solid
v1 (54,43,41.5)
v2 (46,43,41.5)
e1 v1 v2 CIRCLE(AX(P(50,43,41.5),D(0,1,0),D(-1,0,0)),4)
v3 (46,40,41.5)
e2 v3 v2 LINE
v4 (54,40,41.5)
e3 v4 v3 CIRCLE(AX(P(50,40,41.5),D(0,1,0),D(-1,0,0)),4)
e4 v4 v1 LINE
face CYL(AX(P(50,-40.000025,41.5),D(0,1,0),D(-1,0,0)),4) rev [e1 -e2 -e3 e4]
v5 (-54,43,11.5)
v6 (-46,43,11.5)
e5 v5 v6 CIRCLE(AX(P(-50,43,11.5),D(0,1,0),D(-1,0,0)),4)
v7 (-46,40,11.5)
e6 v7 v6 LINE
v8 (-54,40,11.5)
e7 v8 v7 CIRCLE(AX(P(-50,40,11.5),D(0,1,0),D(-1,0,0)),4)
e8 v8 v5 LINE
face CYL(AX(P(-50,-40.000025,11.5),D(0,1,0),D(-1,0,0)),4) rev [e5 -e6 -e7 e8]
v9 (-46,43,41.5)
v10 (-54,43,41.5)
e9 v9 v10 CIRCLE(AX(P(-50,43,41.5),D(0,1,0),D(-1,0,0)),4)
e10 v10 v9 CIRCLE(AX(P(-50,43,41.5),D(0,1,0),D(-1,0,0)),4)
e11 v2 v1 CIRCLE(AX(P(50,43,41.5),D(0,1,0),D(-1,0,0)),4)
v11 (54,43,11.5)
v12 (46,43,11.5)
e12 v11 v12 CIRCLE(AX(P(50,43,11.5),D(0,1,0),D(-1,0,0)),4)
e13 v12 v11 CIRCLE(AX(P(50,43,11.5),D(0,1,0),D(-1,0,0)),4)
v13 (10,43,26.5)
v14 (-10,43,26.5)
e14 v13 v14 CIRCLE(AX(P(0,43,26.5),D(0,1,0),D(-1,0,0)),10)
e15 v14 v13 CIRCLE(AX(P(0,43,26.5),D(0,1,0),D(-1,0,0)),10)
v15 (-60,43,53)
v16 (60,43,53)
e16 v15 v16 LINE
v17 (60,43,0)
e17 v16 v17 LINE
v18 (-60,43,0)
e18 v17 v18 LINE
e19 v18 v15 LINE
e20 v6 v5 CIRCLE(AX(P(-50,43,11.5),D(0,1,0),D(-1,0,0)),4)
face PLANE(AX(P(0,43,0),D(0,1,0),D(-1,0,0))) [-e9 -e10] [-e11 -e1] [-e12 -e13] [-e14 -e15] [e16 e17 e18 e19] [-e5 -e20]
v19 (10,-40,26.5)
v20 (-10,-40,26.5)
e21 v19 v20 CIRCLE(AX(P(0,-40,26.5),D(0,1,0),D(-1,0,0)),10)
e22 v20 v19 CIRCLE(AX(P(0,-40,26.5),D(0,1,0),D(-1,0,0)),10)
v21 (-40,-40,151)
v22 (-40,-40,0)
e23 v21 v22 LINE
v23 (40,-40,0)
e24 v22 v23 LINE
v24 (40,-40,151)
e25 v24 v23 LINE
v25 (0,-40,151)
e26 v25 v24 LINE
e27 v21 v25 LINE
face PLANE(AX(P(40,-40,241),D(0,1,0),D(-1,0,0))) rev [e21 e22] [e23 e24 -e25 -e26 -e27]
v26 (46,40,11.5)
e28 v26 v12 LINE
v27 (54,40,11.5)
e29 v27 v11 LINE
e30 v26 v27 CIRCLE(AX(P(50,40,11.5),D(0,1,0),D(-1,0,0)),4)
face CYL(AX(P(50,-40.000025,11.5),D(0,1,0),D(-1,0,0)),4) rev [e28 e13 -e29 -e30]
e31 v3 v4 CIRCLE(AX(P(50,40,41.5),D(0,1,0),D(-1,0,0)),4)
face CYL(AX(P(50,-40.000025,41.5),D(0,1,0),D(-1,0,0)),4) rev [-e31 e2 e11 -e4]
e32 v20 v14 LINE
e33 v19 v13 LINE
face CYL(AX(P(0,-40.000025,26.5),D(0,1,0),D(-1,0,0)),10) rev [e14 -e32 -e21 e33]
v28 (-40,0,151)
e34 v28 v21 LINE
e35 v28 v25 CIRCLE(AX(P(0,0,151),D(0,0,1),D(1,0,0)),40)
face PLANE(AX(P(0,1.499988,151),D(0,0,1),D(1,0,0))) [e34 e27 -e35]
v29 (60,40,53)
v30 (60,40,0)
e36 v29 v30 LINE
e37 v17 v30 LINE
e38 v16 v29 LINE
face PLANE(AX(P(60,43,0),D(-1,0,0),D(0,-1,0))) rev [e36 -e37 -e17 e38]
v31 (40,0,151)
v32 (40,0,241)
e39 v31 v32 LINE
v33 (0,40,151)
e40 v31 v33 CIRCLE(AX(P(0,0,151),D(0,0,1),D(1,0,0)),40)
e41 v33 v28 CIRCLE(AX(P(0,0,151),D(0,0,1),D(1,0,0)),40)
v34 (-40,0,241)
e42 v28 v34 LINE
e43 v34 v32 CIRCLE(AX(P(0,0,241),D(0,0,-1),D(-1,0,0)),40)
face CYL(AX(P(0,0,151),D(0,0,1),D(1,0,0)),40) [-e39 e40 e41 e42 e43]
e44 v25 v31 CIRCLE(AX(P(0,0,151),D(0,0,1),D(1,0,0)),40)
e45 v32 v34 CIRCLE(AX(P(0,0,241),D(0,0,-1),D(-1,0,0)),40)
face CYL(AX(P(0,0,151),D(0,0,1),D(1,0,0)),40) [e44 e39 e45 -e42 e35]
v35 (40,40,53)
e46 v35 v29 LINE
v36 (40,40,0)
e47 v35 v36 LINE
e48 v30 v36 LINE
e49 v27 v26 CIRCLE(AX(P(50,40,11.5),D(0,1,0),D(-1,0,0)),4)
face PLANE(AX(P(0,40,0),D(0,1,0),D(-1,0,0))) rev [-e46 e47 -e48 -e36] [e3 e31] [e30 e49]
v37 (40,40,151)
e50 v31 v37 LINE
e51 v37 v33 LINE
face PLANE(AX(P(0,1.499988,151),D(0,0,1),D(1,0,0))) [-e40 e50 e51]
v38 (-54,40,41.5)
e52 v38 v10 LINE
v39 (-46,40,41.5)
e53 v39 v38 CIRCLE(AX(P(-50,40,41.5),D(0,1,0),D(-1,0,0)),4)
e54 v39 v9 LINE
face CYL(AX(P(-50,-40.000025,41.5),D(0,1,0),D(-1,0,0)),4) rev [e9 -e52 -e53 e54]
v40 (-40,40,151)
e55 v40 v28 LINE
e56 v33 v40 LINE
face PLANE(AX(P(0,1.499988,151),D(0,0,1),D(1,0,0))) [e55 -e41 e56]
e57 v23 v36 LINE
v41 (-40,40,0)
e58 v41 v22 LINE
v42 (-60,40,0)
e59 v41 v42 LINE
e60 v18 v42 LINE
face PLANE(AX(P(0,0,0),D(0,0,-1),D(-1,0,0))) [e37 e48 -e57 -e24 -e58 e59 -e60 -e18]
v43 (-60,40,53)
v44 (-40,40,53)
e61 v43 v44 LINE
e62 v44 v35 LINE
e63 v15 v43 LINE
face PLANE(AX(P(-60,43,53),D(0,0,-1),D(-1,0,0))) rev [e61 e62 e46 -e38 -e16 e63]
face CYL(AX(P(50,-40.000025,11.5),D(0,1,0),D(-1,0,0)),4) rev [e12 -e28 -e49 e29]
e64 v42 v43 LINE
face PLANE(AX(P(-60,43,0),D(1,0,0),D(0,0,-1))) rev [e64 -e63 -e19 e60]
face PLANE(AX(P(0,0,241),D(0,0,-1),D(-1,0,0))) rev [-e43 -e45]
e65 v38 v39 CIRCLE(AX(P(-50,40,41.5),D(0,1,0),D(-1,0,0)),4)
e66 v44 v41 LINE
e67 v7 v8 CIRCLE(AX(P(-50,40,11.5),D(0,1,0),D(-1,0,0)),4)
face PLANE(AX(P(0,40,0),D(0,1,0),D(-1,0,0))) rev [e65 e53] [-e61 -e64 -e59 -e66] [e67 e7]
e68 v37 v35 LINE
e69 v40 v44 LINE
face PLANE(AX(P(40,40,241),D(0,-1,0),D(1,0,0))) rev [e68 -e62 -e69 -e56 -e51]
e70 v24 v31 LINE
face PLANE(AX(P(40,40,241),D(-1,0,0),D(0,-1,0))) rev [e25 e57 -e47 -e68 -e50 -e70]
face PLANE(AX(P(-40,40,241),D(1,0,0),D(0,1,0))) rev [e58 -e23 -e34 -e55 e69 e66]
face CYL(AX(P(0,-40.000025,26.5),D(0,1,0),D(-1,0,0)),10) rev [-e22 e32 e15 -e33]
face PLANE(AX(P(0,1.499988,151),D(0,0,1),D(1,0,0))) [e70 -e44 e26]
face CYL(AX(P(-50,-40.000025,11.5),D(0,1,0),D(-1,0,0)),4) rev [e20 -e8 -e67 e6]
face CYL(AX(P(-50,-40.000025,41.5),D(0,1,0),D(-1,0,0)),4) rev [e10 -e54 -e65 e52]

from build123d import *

# Parameters (mm, degrees)
SKETCH_1_W          = 80
SKETCH_1_H          = 80
EXTRUDE_1_DEPTH     = 241
SKETCH_2_W          = 120
SKETCH_2_H          = 53
EXTRUDE_2_DEPTH     = 3
SKETCH_3_R          = 4
CUT_EXTRUDE_1_DEPTH = 262.858740545
SKETCH_4_R          = 10
CUT_EXTRUDE_2_DEPTH = 262.858740545
SKETCH_5_OUTSIDE_W  = 178.346
SKETCH_5_OUTSIDE_H  = 141.346
SKETCH_5_OUTSIDE_R  = 40
CUT_EXTRUDE_3_DEPTH = 90


with BuildPart() as part:
    # 草图1 → 凸台-拉伸1 (new body)
    with BuildSketch(Plane.XY):
        Rectangle(SKETCH_1_W, SKETCH_1_H)
    extrude(amount=EXTRUDE_1_DEPTH)

    # 草图2 → 凸台-拉伸2 (add)
    with BuildSketch(Plane(origin=(0, 40, 0), x_dir=(1, 0, 0), z_dir=(0, 1, 0))):
        with Locations((0, -26.5)):
            Rectangle(SKETCH_2_W, SKETCH_2_H)
    extrude(amount=EXTRUDE_2_DEPTH)

    # 草图3 → 切除-拉伸1 (cut, through all)
    with BuildSketch(Plane(origin=(0, 43, 0), x_dir=(1, 0, 0), z_dir=(0, 1, 0))):
        with Locations(Location((-50, -11.5, 0), (0, 0, 180))):
            Circle(SKETCH_3_R)
        with Locations(Location((50, -11.5, 0), (0, 0, 180))):
            Circle(SKETCH_3_R)
        with Locations(Location((50, -41.5, 0), (0, 0, 180))):
            Circle(SKETCH_3_R)
        with Locations(Location((-50, -41.5, 0), (0, 0, 180))):
            Circle(SKETCH_3_R)
    extrude(amount=-CUT_EXTRUDE_1_DEPTH, mode=Mode.SUBTRACT)

    # 草图4 → 切除-拉伸2 (cut, through all)
    with BuildSketch(Plane(origin=(0, 43, 0), x_dir=(1, 0, 0), z_dir=(0, 1, 0))):
        with Locations(Location((0, -26.5, 0), (0, 0, 180))):
            Circle(SKETCH_4_R)
    extrude(amount=-CUT_EXTRUDE_2_DEPTH, mode=Mode.SUBTRACT)

    # 草图5 outside → 切除-拉伸3 (cut)
    with BuildSketch(Plane.XY.offset(241)):
        with Locations((0, 1.5)):
            Rectangle(SKETCH_5_OUTSIDE_W, SKETCH_5_OUTSIDE_H)
        with Locations(Location((0, 0, 0), (0, 0, 180))):
            Circle(SKETCH_5_OUTSIDE_R, mode=Mode.SUBTRACT)
    extrude(amount=-CUT_EXTRUDE_3_DEPTH, mode=Mode.SUBTRACT)


solid = part.part
